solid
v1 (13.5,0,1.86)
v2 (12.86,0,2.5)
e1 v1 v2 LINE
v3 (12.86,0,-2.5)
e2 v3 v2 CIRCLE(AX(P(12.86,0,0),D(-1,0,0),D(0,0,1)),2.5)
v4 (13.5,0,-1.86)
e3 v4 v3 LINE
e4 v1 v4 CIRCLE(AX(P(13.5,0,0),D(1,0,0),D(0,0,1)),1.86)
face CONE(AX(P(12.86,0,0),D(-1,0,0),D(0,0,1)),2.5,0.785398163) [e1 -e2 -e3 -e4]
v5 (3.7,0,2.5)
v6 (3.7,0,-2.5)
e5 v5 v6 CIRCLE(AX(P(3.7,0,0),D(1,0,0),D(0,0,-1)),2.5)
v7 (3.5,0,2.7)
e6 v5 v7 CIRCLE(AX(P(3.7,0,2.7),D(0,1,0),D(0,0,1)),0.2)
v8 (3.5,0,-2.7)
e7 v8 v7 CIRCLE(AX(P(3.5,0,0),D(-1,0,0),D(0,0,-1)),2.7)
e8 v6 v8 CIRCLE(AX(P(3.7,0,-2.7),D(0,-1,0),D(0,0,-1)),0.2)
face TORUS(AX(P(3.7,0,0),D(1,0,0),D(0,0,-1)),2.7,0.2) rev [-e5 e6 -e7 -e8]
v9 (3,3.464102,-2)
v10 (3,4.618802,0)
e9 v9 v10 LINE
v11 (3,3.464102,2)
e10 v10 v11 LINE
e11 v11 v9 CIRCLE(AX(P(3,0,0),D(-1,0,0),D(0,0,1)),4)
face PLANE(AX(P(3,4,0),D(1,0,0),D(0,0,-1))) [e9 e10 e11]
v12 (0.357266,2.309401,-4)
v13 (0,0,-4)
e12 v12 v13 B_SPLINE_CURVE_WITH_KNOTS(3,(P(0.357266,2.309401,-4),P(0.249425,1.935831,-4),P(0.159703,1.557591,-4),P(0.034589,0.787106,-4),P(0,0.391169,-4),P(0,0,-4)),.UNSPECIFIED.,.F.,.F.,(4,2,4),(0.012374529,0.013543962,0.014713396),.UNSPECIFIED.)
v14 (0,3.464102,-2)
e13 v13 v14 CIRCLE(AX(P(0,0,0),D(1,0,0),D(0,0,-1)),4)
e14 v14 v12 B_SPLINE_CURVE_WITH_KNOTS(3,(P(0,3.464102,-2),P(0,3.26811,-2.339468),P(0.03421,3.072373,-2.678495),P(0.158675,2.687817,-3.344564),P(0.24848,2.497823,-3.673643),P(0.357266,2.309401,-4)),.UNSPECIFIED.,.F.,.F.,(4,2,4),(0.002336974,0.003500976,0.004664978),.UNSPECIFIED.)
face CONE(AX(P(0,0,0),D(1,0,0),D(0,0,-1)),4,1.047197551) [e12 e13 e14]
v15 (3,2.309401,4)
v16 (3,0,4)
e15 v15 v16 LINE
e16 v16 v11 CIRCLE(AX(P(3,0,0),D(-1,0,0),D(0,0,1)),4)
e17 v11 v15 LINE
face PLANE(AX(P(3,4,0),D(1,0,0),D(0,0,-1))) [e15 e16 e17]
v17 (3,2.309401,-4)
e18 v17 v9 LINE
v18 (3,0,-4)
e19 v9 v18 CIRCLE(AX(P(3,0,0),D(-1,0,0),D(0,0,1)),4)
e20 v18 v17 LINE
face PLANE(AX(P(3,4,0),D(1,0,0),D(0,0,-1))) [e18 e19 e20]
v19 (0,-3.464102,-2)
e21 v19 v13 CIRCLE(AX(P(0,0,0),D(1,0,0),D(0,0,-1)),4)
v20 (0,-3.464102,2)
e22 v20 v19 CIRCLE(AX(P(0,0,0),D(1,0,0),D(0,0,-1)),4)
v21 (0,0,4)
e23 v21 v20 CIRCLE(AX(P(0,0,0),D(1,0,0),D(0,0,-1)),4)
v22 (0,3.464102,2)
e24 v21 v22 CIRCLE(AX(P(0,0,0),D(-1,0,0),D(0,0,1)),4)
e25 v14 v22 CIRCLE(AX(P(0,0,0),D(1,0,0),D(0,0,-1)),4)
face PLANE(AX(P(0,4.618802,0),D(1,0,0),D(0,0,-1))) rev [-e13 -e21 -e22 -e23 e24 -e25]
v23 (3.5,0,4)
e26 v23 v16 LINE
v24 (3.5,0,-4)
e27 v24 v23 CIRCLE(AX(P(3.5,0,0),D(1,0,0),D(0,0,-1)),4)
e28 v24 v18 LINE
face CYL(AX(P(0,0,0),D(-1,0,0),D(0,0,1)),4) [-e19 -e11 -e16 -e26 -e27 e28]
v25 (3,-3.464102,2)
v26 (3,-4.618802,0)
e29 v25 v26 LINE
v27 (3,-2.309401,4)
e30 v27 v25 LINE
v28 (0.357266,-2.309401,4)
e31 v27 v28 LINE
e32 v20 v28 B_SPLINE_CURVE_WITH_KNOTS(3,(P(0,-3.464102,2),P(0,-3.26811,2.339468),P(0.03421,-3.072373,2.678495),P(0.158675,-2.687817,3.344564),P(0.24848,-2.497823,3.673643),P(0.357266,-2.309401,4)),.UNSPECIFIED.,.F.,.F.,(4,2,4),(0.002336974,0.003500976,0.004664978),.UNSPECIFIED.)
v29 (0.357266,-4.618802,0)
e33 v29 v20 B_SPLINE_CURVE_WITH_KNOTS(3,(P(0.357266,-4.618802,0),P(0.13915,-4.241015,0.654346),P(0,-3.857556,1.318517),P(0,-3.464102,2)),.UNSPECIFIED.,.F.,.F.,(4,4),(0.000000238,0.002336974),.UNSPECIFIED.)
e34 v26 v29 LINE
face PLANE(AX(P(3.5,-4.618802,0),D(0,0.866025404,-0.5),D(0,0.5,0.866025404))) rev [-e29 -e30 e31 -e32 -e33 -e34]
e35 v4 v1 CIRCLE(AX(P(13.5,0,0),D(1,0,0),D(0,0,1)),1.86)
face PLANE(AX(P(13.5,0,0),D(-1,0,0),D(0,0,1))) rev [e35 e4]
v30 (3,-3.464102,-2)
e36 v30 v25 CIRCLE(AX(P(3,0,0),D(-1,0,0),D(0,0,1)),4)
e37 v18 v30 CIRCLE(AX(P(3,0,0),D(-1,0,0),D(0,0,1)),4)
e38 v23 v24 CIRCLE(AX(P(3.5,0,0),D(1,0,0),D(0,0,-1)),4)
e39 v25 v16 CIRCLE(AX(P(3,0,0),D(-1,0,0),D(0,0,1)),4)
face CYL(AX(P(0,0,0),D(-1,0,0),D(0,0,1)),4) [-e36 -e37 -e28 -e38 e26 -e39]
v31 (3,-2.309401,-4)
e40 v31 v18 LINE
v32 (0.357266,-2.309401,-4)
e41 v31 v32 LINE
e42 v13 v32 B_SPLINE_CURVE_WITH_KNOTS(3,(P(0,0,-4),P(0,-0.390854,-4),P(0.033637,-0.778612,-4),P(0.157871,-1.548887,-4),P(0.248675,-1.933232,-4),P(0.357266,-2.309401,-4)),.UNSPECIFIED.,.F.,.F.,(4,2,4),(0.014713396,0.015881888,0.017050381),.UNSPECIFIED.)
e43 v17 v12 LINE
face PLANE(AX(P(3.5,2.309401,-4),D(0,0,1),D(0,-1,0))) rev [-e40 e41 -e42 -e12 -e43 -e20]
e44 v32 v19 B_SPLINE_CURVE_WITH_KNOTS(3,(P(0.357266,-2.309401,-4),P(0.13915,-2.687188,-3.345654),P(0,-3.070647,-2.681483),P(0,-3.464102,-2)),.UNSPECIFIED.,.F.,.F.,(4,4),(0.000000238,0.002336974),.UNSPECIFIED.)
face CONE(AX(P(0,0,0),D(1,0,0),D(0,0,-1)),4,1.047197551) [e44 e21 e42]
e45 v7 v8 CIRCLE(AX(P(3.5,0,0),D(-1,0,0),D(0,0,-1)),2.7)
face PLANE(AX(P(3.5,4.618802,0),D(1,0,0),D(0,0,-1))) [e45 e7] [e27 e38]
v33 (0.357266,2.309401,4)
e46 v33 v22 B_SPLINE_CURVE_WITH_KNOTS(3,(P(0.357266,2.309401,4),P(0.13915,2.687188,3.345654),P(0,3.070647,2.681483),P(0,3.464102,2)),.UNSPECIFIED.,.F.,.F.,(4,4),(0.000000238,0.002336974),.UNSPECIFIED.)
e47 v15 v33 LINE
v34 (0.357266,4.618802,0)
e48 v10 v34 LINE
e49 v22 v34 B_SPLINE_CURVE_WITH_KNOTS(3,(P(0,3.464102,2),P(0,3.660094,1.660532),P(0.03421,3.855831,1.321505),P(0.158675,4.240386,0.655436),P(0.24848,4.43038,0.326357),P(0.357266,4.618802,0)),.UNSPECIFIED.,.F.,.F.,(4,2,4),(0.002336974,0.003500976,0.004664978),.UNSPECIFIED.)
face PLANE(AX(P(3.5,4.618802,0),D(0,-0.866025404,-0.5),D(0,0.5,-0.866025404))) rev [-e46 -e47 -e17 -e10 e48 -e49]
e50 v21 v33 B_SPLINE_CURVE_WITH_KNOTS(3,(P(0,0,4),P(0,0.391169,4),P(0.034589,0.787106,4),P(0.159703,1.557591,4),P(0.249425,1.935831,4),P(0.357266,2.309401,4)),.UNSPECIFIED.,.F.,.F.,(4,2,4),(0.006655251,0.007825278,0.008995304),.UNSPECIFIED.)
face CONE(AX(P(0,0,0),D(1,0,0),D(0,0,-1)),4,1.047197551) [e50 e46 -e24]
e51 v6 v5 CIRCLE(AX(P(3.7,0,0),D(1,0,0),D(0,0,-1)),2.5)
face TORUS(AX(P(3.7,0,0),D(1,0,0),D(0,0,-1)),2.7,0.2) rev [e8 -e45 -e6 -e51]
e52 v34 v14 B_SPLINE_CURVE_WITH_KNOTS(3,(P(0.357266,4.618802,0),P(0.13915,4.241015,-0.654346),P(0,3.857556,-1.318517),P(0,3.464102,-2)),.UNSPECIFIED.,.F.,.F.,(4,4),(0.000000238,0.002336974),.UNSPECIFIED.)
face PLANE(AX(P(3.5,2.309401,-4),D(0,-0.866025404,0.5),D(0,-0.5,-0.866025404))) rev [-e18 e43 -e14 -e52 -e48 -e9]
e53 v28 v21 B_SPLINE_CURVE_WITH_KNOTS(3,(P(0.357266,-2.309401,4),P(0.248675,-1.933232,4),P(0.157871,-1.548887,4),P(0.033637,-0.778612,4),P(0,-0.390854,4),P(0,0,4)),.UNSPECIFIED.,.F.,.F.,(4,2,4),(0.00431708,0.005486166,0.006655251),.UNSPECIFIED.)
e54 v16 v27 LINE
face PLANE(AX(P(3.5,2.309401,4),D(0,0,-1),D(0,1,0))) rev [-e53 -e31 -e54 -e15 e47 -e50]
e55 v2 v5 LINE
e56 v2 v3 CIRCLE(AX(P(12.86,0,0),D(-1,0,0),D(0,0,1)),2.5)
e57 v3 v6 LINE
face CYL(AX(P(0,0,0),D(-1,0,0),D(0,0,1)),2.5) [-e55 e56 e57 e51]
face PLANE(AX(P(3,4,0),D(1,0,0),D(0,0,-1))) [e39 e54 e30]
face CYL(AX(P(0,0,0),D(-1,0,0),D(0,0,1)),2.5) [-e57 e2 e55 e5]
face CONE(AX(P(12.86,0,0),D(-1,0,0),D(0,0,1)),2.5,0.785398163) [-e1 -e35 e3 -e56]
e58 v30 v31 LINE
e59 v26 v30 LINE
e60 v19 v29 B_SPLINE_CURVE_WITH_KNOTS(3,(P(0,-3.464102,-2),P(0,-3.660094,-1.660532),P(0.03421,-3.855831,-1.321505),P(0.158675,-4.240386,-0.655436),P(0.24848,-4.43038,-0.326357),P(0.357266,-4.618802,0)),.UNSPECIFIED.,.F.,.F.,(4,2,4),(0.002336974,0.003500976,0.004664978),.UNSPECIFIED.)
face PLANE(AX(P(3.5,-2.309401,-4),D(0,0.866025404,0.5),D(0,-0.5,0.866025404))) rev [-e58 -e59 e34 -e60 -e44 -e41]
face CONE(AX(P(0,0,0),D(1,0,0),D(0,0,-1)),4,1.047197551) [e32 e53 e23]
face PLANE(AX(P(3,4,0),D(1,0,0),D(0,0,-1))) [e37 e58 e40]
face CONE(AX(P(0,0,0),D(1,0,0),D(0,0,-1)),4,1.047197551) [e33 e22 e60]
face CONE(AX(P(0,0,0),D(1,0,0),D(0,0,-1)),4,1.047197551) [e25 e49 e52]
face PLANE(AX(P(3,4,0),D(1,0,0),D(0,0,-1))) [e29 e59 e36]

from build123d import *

# Parameters (mm, degrees)
BASE_EXTRUDE_DEPTH = 3.5
SKETCH4_W          = 0.5
SKETCH4_H          = 10.618802154
CHAMFER_2_SIZE     = 0.64
FILLET_2_R         = 0.2


with BuildPart() as part:
    # Sketch1 → Base-Extrude (new body)
    with BuildSketch(Plane(origin=(0, 0, 0), x_dir=(0, 0, -1), z_dir=(1, 0, 0))):
        Polygon((4, 2.309401077), (4, -2.309401077), (0, -4.618802154), (-4, -2.309401077), (-4, 2.309401077), (0, 4.618802154), align=None)
    extrude(amount=BASE_EXTRUDE_DEPTH)

    # Sketch2 → Boss-Revolve1 (revolve)
    with BuildSketch(Plane.XY, mode=Mode.PRIVATE) as boss_revolve1_sk:
        Polygon((0, 0), (13.5, 0), (13.5, 1.8072), (13.5, 2.5), (0, 2.5), align=None)
    revolve(boss_revolve1_sk.sketch.rotate(Axis((0, 0, 0), (1, 0, 0)), 90), axis=Axis((0, 0, 0), (1, 0, 0)))

    # Sketch3 → Cut-Revolve1 (revolve, cut)
    with BuildSketch(Plane.XY):
        Polygon((0, 4), (3.244016936, 9.618802154), (3.244016936, 14.618802154), (-10, 14.618802154), (-10, 4), align=None)
    revolve(axis=Axis((0, 0, 0), (1, 0, 0)), mode=Mode.SUBTRACT)

    # Sketch5 → Cut-Revolve2 (revolve, cut)
    with BuildSketch(Plane.XY):
        Polygon((3.5, 4), (0.255983064, 9.618802154), (0.255983064, 14.618802154), (10.255983064, 14.618802154), (10.255983064, 4), align=None)
    revolve(axis=Axis((0, 0, 0), (1, 0, 0)), mode=Mode.SUBTRACT)

    # Sketch4 → Cut-Revolve3 (revolve, cut)
    with BuildSketch(Plane.XY, mode=Mode.PRIVATE) as cut_revolve3_sk:
        with Locations((3.25, 9.309401077)):
            Rectangle(SKETCH4_W, SKETCH4_H)
    revolve(cut_revolve3_sk.sketch.rotate(Axis((0, 0, 0), (1, 0, 0)), 270), axis=Axis((0, 0, 0), (1, 0, 0)), mode=Mode.SUBTRACT)

    # Chamfer 2
    chamfer_2_edges = [part.edges().sort_by_distance(p)[0] for p in [
        (13.5, 0, -2.5),
    ]]
    chamfer(chamfer_2_edges, length=CHAMFER_2_SIZE)

    # Fillet 2
    fillet_2_edges = [part.edges().sort_by_distance(p)[0] for p in [
        (3.5, 0, -2.5),
    ]]
    fillet(fillet_2_edges, radius=FILLET_2_R)


solid = part.part
